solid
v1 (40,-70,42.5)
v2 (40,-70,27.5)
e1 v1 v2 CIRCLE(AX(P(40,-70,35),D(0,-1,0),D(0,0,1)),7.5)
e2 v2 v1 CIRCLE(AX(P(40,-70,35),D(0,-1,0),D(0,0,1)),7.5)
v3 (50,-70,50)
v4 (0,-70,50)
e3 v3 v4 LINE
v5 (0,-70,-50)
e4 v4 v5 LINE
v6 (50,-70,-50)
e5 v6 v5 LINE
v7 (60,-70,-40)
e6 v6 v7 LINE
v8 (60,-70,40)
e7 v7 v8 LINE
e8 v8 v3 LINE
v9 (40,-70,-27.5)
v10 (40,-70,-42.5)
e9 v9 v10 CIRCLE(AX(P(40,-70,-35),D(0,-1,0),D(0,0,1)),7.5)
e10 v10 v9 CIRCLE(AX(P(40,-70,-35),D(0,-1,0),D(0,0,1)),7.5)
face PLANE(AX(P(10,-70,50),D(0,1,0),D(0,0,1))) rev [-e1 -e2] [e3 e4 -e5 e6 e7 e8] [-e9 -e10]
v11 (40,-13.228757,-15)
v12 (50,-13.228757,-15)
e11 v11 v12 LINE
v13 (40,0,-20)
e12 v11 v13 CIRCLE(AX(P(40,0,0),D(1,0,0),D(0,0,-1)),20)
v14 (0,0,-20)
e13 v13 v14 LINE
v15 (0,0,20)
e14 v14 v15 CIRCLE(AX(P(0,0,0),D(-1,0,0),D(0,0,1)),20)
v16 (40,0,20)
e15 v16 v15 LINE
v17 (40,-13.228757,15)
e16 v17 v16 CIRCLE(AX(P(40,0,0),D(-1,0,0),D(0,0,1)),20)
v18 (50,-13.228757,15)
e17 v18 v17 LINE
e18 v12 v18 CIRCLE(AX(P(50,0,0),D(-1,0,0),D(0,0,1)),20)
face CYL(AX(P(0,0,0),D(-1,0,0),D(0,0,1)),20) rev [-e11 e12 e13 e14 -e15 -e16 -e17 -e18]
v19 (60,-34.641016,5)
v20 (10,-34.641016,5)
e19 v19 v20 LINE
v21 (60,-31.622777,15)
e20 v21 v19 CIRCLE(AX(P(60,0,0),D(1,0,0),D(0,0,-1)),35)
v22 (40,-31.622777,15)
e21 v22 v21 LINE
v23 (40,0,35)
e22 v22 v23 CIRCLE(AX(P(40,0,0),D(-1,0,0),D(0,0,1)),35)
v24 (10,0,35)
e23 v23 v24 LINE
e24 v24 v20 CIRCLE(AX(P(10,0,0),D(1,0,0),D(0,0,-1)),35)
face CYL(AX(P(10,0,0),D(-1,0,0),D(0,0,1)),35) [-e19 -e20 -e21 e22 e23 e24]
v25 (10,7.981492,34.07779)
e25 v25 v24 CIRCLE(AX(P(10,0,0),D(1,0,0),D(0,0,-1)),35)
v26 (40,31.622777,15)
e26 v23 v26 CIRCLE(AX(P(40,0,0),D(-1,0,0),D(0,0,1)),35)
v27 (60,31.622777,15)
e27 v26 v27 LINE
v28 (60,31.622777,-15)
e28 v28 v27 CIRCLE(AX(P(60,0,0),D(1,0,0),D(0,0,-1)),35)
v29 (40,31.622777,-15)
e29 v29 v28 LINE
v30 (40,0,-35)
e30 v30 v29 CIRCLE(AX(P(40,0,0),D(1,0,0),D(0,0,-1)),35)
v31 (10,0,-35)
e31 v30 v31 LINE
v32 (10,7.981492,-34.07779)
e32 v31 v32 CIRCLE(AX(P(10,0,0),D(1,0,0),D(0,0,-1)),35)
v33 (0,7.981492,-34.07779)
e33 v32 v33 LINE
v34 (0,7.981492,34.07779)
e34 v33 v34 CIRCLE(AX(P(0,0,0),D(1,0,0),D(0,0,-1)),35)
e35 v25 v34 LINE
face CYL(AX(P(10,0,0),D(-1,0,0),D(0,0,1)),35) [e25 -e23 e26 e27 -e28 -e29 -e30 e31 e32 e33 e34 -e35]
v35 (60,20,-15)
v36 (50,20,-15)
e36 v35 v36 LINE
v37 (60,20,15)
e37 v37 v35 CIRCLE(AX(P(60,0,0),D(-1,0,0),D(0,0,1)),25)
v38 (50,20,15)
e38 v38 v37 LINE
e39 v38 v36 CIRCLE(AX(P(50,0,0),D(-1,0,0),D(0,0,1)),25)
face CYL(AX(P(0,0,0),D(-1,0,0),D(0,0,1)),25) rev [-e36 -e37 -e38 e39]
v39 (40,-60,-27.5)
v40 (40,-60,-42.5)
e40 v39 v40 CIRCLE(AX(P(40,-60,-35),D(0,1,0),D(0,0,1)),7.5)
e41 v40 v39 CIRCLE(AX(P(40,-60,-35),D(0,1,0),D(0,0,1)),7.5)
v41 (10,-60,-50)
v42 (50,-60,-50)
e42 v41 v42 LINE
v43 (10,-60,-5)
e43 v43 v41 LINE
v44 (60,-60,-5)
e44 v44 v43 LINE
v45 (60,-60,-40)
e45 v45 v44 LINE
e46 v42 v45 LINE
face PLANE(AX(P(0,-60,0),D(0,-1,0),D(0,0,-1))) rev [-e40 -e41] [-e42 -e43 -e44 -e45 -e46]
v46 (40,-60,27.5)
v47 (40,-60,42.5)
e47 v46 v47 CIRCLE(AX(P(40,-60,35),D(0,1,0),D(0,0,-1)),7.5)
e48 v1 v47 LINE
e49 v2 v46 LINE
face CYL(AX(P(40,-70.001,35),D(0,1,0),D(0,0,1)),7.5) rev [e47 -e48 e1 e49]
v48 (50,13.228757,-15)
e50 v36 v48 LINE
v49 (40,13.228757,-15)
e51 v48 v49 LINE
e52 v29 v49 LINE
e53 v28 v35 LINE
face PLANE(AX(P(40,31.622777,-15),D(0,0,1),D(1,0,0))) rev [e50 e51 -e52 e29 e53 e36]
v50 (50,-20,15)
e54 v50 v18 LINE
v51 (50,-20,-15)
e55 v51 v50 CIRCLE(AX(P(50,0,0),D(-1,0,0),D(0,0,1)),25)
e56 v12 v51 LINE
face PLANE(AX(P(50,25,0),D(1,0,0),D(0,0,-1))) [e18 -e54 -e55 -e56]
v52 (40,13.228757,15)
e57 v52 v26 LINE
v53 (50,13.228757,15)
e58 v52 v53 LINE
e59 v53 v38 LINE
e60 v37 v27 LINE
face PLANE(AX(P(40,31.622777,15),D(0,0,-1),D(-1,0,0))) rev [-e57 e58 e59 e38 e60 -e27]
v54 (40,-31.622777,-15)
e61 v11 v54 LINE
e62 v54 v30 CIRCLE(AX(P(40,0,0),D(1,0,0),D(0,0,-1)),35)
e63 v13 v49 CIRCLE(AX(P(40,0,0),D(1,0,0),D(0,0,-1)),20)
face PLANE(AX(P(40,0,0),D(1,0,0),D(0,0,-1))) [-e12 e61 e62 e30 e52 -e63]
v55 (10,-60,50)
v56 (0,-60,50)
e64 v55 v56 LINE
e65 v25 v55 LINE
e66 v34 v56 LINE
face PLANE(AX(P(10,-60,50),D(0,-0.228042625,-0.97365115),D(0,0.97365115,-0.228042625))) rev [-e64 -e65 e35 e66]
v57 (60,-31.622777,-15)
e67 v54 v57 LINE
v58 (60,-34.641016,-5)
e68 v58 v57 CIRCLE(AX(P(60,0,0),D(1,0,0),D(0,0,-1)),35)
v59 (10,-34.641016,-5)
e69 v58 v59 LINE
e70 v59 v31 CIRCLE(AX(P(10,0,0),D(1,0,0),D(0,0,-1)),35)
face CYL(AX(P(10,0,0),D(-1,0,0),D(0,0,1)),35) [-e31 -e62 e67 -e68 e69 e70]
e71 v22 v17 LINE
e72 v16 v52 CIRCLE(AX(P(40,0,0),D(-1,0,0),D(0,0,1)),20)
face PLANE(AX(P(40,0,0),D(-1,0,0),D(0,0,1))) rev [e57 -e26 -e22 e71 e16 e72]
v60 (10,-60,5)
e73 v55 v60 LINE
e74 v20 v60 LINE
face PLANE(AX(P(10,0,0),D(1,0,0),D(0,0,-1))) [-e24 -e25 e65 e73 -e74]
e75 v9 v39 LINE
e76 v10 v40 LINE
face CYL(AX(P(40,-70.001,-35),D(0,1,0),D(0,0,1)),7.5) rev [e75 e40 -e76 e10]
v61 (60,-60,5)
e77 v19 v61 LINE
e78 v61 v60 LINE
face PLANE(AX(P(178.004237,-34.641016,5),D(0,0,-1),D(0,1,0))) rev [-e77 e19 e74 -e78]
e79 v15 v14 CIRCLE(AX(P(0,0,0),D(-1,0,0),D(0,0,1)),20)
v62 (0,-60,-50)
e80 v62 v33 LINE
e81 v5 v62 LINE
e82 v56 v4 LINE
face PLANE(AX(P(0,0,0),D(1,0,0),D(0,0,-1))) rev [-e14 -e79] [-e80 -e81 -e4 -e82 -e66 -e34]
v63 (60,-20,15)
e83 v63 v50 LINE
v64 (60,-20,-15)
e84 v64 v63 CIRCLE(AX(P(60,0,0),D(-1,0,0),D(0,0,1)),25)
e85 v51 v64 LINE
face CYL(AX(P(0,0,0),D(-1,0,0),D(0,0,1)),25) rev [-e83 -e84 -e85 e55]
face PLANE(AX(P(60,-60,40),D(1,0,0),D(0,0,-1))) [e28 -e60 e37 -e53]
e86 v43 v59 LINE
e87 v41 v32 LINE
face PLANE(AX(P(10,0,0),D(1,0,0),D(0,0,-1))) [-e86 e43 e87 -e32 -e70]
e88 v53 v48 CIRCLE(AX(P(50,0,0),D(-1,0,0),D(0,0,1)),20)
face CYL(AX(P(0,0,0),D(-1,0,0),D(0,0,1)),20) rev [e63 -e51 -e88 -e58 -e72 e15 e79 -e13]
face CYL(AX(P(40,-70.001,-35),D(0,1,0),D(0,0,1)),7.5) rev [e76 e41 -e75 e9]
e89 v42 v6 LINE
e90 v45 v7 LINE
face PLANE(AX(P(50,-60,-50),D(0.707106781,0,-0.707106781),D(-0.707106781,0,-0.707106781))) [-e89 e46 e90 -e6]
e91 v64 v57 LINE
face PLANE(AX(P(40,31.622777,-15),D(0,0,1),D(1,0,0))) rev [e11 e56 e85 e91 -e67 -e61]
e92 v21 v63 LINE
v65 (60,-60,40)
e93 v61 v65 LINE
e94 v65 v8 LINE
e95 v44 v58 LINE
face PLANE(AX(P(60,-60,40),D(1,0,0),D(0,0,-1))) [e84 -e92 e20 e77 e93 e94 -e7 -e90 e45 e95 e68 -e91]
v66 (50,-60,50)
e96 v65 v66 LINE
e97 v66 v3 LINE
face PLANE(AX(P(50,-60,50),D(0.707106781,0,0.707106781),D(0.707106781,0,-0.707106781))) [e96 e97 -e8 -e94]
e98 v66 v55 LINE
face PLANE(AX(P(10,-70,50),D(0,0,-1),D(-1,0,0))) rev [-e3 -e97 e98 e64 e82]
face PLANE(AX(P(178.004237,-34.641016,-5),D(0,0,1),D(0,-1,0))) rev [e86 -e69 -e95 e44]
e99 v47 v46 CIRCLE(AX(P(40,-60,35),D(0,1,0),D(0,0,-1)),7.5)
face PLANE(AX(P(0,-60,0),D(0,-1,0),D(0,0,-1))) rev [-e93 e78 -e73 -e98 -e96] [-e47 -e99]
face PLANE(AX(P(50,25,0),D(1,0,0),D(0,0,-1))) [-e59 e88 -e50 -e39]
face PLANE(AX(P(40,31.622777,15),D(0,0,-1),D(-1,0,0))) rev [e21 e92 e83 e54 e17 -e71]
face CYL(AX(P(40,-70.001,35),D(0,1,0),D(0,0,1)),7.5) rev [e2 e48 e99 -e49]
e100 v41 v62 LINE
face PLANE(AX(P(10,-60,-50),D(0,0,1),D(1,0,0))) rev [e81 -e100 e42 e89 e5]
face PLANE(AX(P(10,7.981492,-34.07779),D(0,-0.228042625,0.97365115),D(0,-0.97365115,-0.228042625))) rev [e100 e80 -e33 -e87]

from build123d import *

# Parameters (mm, degrees)
BACK_PLATE_DEPTH        = 10
BASE_PLATE_DEPTH        = 10
HOUSING_BOSS_DEPTH      = 50
MOUNTING_HOLES_REACH    = 124.984
MOUNTING_HOLES_SKETCH_R = 7.5
HOUSING_SLOT_PROFILE_W  = 28.353660078
HOUSING_SLOT_PROFILE_H  = 63.245553204
HOUSING_SLOT_CUT_DEPTH  = 20


with BuildPart() as part:
    # Back Plate Profile → Back Plate (new body)
    with BuildSketch(Plane(origin=(0, 0, 0), x_dir=(0, 0, -1), z_dir=(1, 0, 0))):
        with BuildLine():
            Line((-50, -70), (50, -70))
            Line((50, -70), (50, -60))
            Line((50, -60), (34.077790239, 7.981491866))
            ThreePointArc((34.077790239, 7.981491866), (0, 35), (-34.077790239, 7.981491866))
            Line((-34.077790239, 7.981491866), (-50, -60))
            Line((-50, -60), (-50, -70))
        make_face()
    extrude(amount=BACK_PLATE_DEPTH)

    # Base Plate Profile → Base Plate (add)
    with BuildSketch(Plane.XZ.offset(70)):
        Polygon((10, 50), (50, 50), (60, 40), (60, -40), (50, -50), (10, -50), align=None)
    extrude(amount=-BASE_PLATE_DEPTH)

    # Housing Boss Profile → Housing Boss (add)
    with BuildSketch(Plane(origin=(10, 0, 0), x_dir=(0, 0, -1), z_dir=(1, 0, 0))):
        with BuildLine():
            Line((-5, -34.641016151), (-5, -60))
            Line((-5, -60), (5, -60))
            Line((5, -60), (5, -34.641016151))
            ThreePointArc((5, -34.641016151), (0, 35), (-5, -34.641016151))
        make_face()
    extrude(amount=HOUSING_BOSS_DEPTH)

    # Mounting Holes Sketch → Mounting Holes (cut, up to next)
    with BuildSketch(Plane(origin=(0, -60, 0), x_dir=(1, 0, 0), z_dir=(0, 1, 0)), mode=Mode.PRIVATE) as mounting_holes_sk1:
        with Locations(Location((40, 35, 0), (0, 0, 270))):
            Circle(MOUNTING_HOLES_SKETCH_R)
    mounting_holes_tool1 = extrude(mounting_holes_sk1.sketch, amount=-MOUNTING_HOLES_REACH, mode=Mode.PRIVATE) & part.part
    # Mounting Holes Sketch → Mounting Holes (cut, up to next)
    with BuildSketch(Plane(origin=(0, -60, 0), x_dir=(1, 0, 0), z_dir=(0, 1, 0)), mode=Mode.PRIVATE) as mounting_holes_sk2:
        with Locations(Location((40, -35, 0), (0, 0, 270))):
            Circle(MOUNTING_HOLES_SKETCH_R)
    mounting_holes_tool2 = extrude(mounting_holes_sk2.sketch, amount=-MOUNTING_HOLES_REACH, mode=Mode.PRIVATE) & part.part
    add(mounting_holes_tool1.solids().sort_by_distance((40, -60, -35))[0], mode=Mode.SUBTRACT)
    add(mounting_holes_tool2.solids().sort_by_distance((40, -60, 35))[0], mode=Mode.SUBTRACT)

    # Gland Bore Profile → Gland Bore (revolve, cut)
    with BuildSketch(Plane.XY, mode=Mode.PRIVATE) as gland_bore_sk:
        Polygon((0, 0), (60, 0), (60, 25), (50, 25), (50, 20), (40, 20), (0, 20), align=None)
    revolve(gland_bore_sk.sketch.rotate(Axis((0, 0, 0), (1, 0, 0)), 90), axis=Axis((0, 0, 0), (1, 0, 0)), mode=Mode.SUBTRACT)

    # Housing Slot Profile → Housing Slot Cut (cut)
    with BuildSketch(Plane(origin=(60, 0, 0), x_dir=(0, 0, -1), z_dir=(1, 0, 0))):
        with Locations((-29.176830039, 0)):
            Rectangle(HOUSING_SLOT_PROFILE_W, HOUSING_SLOT_PROFILE_H)
        with Locations((29.176830039, 0)):
            Rectangle(HOUSING_SLOT_PROFILE_W, HOUSING_SLOT_PROFILE_H)
    extrude(amount=-HOUSING_SLOT_CUT_DEPTH, mode=Mode.SUBTRACT)


solid = part.part
